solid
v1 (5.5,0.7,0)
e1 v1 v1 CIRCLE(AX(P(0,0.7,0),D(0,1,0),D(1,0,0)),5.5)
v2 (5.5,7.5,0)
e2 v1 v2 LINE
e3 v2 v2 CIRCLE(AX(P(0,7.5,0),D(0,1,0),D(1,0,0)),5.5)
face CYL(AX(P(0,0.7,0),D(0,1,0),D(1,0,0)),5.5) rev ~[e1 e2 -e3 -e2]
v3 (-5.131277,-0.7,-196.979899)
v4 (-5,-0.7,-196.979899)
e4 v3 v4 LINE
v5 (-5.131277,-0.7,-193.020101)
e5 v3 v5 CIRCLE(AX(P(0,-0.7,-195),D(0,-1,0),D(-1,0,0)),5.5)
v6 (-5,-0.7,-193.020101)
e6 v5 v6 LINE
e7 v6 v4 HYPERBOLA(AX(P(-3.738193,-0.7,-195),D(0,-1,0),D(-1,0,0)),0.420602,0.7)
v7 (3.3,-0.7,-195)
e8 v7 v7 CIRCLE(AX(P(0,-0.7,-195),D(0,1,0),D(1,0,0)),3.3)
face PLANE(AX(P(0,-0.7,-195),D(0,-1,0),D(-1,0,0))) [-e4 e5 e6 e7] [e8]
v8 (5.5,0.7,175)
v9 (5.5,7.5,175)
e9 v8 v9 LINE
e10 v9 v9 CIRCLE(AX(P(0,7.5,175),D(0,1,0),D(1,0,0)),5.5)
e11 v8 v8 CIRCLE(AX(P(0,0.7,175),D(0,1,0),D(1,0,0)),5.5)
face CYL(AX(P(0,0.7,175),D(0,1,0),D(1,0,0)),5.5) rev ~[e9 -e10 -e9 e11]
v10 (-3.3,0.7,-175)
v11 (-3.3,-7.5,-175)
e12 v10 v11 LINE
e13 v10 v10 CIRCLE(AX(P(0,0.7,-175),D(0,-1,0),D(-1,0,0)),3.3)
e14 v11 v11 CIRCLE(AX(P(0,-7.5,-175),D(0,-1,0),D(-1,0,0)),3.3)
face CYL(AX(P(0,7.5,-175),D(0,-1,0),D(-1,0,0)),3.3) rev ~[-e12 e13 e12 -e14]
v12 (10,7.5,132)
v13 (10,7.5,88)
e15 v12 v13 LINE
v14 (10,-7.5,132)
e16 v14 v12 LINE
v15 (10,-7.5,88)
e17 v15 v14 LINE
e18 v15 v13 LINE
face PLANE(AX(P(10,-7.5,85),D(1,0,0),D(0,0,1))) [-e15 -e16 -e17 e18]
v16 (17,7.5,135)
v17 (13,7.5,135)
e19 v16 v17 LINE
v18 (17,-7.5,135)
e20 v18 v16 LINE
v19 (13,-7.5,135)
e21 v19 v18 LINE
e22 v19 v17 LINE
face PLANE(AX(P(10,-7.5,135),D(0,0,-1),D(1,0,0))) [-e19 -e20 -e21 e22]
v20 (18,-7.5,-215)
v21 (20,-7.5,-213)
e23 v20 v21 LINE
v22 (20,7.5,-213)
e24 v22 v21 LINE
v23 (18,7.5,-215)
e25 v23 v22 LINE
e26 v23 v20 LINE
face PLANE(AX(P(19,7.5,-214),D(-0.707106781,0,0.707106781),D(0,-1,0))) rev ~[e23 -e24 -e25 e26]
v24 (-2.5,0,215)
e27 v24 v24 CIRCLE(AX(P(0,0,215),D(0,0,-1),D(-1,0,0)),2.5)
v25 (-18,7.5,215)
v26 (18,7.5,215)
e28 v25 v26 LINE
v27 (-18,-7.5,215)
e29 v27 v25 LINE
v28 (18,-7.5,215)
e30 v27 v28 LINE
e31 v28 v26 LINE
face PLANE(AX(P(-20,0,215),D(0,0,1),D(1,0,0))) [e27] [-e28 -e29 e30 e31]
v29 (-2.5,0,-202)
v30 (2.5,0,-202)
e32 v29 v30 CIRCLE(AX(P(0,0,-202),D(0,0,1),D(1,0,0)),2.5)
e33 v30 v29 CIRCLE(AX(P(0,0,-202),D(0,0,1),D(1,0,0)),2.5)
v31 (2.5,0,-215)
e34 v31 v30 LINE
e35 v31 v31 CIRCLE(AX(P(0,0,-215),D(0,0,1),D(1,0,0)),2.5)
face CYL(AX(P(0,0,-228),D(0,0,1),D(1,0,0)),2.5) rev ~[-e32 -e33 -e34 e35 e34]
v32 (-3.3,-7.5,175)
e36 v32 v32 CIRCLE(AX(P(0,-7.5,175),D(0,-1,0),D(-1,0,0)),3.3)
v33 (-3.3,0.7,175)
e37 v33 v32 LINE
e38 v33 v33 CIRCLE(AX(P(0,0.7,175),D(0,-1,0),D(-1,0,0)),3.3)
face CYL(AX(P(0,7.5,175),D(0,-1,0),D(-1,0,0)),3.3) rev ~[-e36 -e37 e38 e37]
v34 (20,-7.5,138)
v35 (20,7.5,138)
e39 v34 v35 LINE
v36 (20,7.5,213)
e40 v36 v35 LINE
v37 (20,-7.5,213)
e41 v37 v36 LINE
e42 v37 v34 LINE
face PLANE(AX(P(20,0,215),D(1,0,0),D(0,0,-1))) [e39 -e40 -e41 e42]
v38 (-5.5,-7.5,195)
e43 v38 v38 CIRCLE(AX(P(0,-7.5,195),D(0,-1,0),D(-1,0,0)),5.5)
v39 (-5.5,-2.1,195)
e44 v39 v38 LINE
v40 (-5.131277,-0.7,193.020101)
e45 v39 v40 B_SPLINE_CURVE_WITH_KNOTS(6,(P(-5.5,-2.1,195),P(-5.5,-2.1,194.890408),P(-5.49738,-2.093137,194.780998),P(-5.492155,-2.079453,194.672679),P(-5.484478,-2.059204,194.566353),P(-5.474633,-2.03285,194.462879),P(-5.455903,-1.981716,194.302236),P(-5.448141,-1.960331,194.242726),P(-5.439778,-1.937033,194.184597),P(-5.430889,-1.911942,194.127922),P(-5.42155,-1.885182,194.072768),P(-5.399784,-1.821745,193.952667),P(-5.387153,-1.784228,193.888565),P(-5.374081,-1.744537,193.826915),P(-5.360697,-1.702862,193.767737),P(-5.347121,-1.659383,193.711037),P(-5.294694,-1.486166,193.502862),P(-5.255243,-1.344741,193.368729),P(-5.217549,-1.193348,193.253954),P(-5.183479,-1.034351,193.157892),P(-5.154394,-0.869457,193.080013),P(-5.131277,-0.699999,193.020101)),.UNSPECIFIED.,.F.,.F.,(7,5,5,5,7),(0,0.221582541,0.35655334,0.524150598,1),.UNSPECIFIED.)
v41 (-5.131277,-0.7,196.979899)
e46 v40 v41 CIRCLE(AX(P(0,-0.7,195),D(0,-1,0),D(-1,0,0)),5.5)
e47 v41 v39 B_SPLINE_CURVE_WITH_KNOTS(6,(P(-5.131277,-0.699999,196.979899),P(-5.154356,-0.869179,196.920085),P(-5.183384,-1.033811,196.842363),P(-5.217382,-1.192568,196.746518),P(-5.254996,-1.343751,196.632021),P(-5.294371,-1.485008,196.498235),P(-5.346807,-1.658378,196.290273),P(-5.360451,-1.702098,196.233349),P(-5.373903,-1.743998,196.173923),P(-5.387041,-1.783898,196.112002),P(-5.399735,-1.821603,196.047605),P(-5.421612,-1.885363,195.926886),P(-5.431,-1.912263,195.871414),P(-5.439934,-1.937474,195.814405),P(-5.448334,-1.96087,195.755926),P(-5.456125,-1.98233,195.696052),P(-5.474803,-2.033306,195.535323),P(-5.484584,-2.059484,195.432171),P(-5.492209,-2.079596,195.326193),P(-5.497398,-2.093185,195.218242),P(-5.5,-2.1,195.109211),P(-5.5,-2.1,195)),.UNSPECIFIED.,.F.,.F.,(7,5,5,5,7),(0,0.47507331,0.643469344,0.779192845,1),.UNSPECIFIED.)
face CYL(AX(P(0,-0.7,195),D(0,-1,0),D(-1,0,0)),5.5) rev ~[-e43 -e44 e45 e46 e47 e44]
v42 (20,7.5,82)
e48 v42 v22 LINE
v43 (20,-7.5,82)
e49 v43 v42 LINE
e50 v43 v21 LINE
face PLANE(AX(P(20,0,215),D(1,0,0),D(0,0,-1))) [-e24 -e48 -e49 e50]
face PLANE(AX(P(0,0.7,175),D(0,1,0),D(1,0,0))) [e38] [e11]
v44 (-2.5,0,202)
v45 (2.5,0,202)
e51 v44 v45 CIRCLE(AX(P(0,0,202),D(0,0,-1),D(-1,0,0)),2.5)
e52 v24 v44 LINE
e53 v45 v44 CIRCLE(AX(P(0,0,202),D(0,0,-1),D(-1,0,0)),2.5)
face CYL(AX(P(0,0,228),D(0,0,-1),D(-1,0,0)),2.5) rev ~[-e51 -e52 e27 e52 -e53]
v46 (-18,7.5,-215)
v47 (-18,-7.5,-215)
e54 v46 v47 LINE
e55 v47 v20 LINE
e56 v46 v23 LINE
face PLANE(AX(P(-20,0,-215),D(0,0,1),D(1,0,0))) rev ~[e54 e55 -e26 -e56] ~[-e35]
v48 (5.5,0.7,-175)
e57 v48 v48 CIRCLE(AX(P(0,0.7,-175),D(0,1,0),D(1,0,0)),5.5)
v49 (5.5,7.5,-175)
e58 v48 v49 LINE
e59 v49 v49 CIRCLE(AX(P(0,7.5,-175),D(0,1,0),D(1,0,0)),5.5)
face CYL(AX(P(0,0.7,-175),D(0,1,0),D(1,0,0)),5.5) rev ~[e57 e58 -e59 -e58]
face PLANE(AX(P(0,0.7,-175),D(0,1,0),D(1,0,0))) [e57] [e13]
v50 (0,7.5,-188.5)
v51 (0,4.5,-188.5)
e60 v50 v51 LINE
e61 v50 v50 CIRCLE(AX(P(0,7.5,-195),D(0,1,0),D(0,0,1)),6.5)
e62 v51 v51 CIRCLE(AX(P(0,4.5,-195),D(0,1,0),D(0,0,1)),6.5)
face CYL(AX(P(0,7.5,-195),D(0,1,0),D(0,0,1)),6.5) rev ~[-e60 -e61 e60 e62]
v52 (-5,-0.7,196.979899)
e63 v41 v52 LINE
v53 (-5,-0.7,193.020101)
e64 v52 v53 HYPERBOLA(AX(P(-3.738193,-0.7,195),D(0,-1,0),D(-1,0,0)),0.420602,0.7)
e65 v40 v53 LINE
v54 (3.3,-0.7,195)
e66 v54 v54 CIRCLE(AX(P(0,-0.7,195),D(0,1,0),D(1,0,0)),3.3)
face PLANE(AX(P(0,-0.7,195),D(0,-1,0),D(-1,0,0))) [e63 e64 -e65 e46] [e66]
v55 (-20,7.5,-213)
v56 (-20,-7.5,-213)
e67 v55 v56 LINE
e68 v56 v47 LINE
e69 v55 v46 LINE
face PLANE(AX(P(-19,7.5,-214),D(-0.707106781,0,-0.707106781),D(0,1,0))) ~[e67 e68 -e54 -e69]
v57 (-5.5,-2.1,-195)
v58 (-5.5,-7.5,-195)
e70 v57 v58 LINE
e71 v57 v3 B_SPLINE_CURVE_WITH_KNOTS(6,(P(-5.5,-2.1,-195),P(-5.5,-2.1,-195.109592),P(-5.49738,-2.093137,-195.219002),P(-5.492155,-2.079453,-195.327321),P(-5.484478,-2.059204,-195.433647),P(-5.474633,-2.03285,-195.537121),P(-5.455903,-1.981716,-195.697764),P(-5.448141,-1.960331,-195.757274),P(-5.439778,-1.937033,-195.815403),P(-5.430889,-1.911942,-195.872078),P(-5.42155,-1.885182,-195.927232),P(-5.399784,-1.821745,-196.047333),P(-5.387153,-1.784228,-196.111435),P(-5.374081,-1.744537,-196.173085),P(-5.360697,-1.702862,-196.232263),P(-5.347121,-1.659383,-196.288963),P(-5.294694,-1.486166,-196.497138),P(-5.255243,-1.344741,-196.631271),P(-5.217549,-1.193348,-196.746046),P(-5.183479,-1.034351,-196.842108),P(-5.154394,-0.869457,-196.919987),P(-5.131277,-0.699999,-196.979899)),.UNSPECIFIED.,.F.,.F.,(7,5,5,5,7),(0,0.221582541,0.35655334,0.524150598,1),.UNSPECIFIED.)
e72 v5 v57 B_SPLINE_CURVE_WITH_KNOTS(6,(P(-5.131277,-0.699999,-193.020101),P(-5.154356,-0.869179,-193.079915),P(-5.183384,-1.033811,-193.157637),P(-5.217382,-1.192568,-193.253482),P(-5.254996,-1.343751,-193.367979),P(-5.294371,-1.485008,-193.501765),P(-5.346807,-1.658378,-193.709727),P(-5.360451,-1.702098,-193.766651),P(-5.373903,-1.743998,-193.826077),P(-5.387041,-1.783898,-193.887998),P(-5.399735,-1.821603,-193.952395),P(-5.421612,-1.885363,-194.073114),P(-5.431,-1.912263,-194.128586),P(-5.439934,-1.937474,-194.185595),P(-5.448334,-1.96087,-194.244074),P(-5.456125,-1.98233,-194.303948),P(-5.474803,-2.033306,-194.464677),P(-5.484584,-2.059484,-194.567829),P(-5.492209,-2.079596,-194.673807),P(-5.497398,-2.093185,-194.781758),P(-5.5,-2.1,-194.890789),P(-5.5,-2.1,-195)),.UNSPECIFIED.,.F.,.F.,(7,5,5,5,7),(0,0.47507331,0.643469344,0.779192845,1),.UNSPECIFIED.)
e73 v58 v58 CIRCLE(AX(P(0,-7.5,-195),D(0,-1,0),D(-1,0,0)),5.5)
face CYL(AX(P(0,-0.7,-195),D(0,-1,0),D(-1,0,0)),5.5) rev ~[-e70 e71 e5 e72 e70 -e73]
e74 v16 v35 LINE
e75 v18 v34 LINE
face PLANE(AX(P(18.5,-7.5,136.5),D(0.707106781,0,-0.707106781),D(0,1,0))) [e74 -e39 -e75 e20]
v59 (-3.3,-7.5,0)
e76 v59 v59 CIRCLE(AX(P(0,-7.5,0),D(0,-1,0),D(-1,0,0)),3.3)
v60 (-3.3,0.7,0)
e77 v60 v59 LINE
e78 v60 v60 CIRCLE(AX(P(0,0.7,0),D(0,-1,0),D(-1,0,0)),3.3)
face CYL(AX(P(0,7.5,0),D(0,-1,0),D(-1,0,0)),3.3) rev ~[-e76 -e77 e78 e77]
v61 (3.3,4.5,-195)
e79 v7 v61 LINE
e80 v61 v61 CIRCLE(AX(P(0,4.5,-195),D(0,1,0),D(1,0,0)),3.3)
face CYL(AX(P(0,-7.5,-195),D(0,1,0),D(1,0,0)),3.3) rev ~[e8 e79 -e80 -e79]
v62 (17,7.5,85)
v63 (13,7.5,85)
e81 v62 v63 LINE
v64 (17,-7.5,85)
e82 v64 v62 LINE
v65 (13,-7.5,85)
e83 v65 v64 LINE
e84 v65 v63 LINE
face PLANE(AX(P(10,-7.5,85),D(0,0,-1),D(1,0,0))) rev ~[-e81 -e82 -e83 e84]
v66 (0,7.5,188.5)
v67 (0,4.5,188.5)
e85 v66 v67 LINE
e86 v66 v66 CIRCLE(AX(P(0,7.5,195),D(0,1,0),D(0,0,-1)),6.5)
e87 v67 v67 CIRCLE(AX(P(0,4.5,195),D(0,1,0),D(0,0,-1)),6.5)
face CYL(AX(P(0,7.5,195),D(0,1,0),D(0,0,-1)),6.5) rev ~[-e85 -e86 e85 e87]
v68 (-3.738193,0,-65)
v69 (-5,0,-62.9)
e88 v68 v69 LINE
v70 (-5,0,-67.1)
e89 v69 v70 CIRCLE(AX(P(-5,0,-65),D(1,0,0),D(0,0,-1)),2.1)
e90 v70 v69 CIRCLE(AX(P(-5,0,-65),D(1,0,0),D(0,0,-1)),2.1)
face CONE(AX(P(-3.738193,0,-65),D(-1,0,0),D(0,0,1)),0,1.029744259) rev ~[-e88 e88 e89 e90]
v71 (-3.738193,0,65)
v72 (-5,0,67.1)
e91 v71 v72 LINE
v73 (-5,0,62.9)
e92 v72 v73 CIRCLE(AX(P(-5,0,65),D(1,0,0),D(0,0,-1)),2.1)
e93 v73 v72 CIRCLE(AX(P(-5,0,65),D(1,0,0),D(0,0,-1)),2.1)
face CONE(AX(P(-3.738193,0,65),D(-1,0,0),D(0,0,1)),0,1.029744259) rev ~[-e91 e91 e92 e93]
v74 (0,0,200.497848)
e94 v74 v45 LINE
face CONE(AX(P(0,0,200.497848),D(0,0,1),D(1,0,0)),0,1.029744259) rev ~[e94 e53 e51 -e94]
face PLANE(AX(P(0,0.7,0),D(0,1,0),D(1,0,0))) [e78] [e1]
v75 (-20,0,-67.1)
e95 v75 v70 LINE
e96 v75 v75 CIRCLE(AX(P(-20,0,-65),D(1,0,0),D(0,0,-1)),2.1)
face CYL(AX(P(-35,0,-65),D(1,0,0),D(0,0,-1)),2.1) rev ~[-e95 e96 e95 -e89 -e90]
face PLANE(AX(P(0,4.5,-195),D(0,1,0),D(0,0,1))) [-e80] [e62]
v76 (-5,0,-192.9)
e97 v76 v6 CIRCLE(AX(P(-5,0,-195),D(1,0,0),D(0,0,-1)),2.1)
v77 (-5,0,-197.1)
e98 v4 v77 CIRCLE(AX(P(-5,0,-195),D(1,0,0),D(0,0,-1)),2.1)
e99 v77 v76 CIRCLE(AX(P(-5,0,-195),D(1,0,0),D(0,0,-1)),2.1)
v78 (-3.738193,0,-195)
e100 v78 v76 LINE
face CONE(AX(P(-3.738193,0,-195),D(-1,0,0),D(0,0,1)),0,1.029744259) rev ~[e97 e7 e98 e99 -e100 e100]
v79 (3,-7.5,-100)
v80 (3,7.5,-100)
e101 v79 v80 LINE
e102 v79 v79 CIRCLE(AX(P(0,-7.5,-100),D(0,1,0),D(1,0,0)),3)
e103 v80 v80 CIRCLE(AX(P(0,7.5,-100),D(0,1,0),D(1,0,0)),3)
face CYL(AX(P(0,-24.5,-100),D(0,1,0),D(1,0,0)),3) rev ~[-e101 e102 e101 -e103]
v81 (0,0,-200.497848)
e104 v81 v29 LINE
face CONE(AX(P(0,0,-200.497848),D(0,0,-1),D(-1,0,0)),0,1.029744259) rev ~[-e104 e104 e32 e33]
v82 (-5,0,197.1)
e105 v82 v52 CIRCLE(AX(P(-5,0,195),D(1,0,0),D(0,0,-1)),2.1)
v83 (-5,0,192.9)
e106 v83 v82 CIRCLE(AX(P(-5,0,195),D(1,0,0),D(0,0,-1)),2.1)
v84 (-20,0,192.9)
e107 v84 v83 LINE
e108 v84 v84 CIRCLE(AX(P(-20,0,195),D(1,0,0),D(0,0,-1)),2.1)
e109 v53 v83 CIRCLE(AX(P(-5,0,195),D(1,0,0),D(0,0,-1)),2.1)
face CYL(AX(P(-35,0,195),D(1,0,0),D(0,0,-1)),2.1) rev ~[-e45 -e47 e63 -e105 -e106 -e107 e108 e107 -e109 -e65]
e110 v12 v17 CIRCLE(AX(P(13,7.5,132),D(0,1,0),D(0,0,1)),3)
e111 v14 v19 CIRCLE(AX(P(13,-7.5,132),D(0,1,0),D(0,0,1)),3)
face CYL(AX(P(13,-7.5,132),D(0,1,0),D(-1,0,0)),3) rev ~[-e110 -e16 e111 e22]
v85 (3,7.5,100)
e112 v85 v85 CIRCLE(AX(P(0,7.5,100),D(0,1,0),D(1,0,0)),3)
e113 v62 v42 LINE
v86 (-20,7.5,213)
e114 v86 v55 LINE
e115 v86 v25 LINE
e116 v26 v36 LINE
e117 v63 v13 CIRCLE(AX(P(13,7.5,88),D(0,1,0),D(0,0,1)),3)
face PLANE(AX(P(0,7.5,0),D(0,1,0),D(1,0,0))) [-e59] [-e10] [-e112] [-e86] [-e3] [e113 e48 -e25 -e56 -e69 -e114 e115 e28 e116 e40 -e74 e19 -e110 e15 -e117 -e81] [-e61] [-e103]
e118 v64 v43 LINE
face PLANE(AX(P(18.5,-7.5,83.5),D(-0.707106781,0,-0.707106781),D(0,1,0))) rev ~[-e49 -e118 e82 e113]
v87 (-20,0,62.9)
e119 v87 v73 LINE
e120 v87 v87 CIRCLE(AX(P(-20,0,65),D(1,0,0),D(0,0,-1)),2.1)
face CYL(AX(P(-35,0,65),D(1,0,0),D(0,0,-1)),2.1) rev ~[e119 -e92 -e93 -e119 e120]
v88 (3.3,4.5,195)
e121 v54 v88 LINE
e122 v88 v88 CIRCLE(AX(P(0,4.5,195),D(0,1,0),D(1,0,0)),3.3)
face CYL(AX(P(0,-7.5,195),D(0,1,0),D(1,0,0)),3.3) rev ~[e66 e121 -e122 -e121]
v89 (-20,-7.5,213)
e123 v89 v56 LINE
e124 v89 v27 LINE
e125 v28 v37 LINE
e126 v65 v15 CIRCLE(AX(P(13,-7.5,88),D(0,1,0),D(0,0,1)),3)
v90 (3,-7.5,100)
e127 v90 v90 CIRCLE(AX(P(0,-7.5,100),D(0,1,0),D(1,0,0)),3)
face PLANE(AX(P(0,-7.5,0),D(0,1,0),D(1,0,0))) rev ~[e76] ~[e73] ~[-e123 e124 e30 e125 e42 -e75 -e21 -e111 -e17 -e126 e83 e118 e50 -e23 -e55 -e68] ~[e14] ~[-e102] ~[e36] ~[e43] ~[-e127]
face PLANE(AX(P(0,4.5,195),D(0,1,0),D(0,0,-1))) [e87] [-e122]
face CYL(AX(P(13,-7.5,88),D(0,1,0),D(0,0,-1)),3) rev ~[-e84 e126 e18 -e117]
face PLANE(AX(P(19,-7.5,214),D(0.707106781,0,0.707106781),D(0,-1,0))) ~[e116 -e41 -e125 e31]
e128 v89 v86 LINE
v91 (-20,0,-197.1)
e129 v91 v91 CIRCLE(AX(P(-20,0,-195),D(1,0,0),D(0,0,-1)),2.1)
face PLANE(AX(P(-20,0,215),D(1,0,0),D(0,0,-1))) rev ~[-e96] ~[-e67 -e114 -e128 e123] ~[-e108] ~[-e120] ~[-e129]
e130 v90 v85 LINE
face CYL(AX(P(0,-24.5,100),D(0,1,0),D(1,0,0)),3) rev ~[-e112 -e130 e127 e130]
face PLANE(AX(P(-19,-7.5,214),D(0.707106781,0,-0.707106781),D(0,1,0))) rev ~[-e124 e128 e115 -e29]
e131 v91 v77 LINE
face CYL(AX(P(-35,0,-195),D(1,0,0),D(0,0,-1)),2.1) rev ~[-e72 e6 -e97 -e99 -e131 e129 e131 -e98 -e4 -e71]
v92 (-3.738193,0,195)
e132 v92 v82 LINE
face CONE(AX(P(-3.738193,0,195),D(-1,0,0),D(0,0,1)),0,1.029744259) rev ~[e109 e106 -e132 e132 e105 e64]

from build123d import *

# Parameters (mm, degrees)
SKETCH1_W                                    = 40
SKETCH1_H                                    = 430
BOSS_EXTRUDE1_DEPTH                          = 7.5
SKETCH2_R                                    = 6.5
CUT_EXTRUDE1_DEPTH                           = 3
HEX_SOCKET_CAP_SCREW_HOLE_TYPE_1_D           = 6.6
HEX_SOCKET_CAP_SCREW_HOLE_TYPE_1_CBORE_D     = 11
HEX_SOCKET_CAP_SCREW_HOLE_TYPE_1_CBORE_DEPTH = 6.8
M5_TAPPED_HOLE1_D                            = 4.2
M5_TAPPED_HOLE1_DEPTH                        = 15
M5_TAPPED_HOLE1_TIP                          = 1.2618073
CHAMFER1_SIZE                                = 2
HEX_SOCKET_CAP_SCREW_HOLE_TYPE_2_D           = 6.6
HEX_SOCKET_CAP_SCREW_HOLE_TYPE_2_CBORE_D     = 11
HEX_SOCKET_CAP_SCREW_HOLE_TYPE_2_CBORE_DEPTH = 6.8
M6_TAPPED_HOLE1_D                            = 5
M6_TAPPED_HOLE1_DEPTH                        = 13
M6_TAPPED_HOLE1_TIP                          = 1.502151548
M6_TAPPED_HOLE2_D                            = 5
M6_TAPPED_HOLE2_DEPTH                        = 13
M6_TAPPED_HOLE2_TIP                          = 1.502151548
F_6_0_6_DIAMETER_HOLE1_D                     = 6
F_6_0_6_DIAMETER_HOLE1_DEPTH                 = 17
F_6_0_6_DIAMETER_HOLE1_TIP                   = 1.802581857
SKETCH15_W                                   = 10
SKETCH15_H                                   = 50
CUT_EXTRUDE2_DEPTH                           = 217.448608228
FILLET1_R                                    = 3
CHAMFER2_SIZE                                = 3


with BuildPart() as part:
    # Sketch1 → Boss-Extrude1 (new, symmetric)
    with BuildSketch(Plane(origin=(0, 0, 0), x_dir=(1, 0, 0), z_dir=(0, 1, 0))):
        Rectangle(SKETCH1_W, SKETCH1_H)
    extrude(amount=BOSS_EXTRUDE1_DEPTH, both=True)

    # Sketch2 → Cut-Extrude1 (cut)
    with BuildSketch(Plane(origin=(0, 7.5, 0), x_dir=(1, 0, 0), z_dir=(0, 1, 0))):
        with Locations(Location((0, 195, 0), (0, 0, 270))):
            Circle(SKETCH2_R)
        with Locations(Location((0, -195, 0), (0, 0, 90))):
            Circle(SKETCH2_R)
    extrude(amount=-CUT_EXTRUDE1_DEPTH, mode=Mode.SUBTRACT)

    # Hex socket cap screw hole type 1 (through all)
    with Locations(Plane(origin=(0, -7.5, 0), x_dir=(-1, 0, 0), z_dir=(0, -1, 0))):
        with Locations((0, -195), (0, 195)):
            CounterBoreHole(HEX_SOCKET_CAP_SCREW_HOLE_TYPE_1_D / 2, HEX_SOCKET_CAP_SCREW_HOLE_TYPE_1_CBORE_D / 2, HEX_SOCKET_CAP_SCREW_HOLE_TYPE_1_CBORE_DEPTH)

    # M5 Tapped Hole1
    with Locations(Plane.ZY.offset(20)):
        with Locations((-195, 0), (195, 0), (-65, 0), (65, 0)):
            Hole(M5_TAPPED_HOLE1_D / 2, depth=M5_TAPPED_HOLE1_DEPTH)
            with Locations((0, 0, -(M5_TAPPED_HOLE1_DEPTH + M5_TAPPED_HOLE1_TIP / 2))):  # 118° drill point
                Cone(0, M5_TAPPED_HOLE1_D / 2, M5_TAPPED_HOLE1_TIP, mode=Mode.SUBTRACT)

    # Chamfer1
    chamfer1_edges = [part.edges().sort_by_distance(p)[0] for p in [
        (-20, 0, -215),
        (20, 0, -215),
        (20, 0, 215),
        (-20, 0, 215),
    ]]
    chamfer(chamfer1_edges, length=CHAMFER1_SIZE)

    # Hex socket cap screw hole type 2 (through all)
    with Locations(Plane(origin=(0, 7.5, 0), x_dir=(1, 0, 0), z_dir=(0, 1, 0))):
        with Locations((0, 175), (0, -175), (0, 0)):
            CounterBoreHole(HEX_SOCKET_CAP_SCREW_HOLE_TYPE_2_D / 2, HEX_SOCKET_CAP_SCREW_HOLE_TYPE_2_CBORE_D / 2, HEX_SOCKET_CAP_SCREW_HOLE_TYPE_2_CBORE_DEPTH)

    # M6 Tapped Hole1
    with Locations(Plane.XY.offset(215)):
        with Locations((0, 0)):
            Hole(M6_TAPPED_HOLE1_D / 2, depth=M6_TAPPED_HOLE1_DEPTH)
            with Locations((0, 0, -(M6_TAPPED_HOLE1_DEPTH + M6_TAPPED_HOLE1_TIP / 2))):  # 118° drill point
                Cone(0, M6_TAPPED_HOLE1_D / 2, M6_TAPPED_HOLE1_TIP, mode=Mode.SUBTRACT)

    # M6 Tapped Hole2
    with Locations(Plane(origin=(0, 0, -215), x_dir=(-1, 0, 0), z_dir=(0, 0, -1))):
        with Locations((0, 0)):
            Hole(M6_TAPPED_HOLE2_D / 2, depth=M6_TAPPED_HOLE2_DEPTH)
            with Locations((0, 0, -(M6_TAPPED_HOLE2_DEPTH + M6_TAPPED_HOLE2_TIP / 2))):  # 118° drill point
                Cone(0, M6_TAPPED_HOLE2_D / 2, M6_TAPPED_HOLE2_TIP, mode=Mode.SUBTRACT)

    # Ø6.0 (6) Diameter Hole1
    with Locations(Plane(origin=(0, -7.5, 0), x_dir=(-1, 0, 0), z_dir=(0, -1, 0))):
        with Locations((0, 100), (0, -100)):
            Hole(F_6_0_6_DIAMETER_HOLE1_D / 2, depth=F_6_0_6_DIAMETER_HOLE1_DEPTH)
            with Locations((0, 0, -(F_6_0_6_DIAMETER_HOLE1_DEPTH + F_6_0_6_DIAMETER_HOLE1_TIP / 2))):  # 118° drill point
                Cone(0, F_6_0_6_DIAMETER_HOLE1_D / 2, F_6_0_6_DIAMETER_HOLE1_TIP, mode=Mode.SUBTRACT)

    # Sketch15 → Cut-Extrude2 (cut, through all)
    with BuildSketch(Plane.XZ.offset(7.5)):
        with Locations((15, 110)):
            Rectangle(SKETCH15_W, SKETCH15_H)
    extrude(amount=-CUT_EXTRUDE2_DEPTH, mode=Mode.SUBTRACT)

    # Fillet1
    fillet1_edges = [part.edges().sort_by_distance(p)[0] for p in [
        (10, 0, 85),
        (10, 0, 135),
    ]]
    fillet(fillet1_edges, radius=FILLET1_R)

    # Chamfer2
    chamfer2_edges = [part.edges().sort_by_distance(p)[0] for p in [
        (20, 0, 135),
        (20, 0, 85),
    ]]
    chamfer(chamfer2_edges, length=CHAMFER2_SIZE)


solid = part.part
